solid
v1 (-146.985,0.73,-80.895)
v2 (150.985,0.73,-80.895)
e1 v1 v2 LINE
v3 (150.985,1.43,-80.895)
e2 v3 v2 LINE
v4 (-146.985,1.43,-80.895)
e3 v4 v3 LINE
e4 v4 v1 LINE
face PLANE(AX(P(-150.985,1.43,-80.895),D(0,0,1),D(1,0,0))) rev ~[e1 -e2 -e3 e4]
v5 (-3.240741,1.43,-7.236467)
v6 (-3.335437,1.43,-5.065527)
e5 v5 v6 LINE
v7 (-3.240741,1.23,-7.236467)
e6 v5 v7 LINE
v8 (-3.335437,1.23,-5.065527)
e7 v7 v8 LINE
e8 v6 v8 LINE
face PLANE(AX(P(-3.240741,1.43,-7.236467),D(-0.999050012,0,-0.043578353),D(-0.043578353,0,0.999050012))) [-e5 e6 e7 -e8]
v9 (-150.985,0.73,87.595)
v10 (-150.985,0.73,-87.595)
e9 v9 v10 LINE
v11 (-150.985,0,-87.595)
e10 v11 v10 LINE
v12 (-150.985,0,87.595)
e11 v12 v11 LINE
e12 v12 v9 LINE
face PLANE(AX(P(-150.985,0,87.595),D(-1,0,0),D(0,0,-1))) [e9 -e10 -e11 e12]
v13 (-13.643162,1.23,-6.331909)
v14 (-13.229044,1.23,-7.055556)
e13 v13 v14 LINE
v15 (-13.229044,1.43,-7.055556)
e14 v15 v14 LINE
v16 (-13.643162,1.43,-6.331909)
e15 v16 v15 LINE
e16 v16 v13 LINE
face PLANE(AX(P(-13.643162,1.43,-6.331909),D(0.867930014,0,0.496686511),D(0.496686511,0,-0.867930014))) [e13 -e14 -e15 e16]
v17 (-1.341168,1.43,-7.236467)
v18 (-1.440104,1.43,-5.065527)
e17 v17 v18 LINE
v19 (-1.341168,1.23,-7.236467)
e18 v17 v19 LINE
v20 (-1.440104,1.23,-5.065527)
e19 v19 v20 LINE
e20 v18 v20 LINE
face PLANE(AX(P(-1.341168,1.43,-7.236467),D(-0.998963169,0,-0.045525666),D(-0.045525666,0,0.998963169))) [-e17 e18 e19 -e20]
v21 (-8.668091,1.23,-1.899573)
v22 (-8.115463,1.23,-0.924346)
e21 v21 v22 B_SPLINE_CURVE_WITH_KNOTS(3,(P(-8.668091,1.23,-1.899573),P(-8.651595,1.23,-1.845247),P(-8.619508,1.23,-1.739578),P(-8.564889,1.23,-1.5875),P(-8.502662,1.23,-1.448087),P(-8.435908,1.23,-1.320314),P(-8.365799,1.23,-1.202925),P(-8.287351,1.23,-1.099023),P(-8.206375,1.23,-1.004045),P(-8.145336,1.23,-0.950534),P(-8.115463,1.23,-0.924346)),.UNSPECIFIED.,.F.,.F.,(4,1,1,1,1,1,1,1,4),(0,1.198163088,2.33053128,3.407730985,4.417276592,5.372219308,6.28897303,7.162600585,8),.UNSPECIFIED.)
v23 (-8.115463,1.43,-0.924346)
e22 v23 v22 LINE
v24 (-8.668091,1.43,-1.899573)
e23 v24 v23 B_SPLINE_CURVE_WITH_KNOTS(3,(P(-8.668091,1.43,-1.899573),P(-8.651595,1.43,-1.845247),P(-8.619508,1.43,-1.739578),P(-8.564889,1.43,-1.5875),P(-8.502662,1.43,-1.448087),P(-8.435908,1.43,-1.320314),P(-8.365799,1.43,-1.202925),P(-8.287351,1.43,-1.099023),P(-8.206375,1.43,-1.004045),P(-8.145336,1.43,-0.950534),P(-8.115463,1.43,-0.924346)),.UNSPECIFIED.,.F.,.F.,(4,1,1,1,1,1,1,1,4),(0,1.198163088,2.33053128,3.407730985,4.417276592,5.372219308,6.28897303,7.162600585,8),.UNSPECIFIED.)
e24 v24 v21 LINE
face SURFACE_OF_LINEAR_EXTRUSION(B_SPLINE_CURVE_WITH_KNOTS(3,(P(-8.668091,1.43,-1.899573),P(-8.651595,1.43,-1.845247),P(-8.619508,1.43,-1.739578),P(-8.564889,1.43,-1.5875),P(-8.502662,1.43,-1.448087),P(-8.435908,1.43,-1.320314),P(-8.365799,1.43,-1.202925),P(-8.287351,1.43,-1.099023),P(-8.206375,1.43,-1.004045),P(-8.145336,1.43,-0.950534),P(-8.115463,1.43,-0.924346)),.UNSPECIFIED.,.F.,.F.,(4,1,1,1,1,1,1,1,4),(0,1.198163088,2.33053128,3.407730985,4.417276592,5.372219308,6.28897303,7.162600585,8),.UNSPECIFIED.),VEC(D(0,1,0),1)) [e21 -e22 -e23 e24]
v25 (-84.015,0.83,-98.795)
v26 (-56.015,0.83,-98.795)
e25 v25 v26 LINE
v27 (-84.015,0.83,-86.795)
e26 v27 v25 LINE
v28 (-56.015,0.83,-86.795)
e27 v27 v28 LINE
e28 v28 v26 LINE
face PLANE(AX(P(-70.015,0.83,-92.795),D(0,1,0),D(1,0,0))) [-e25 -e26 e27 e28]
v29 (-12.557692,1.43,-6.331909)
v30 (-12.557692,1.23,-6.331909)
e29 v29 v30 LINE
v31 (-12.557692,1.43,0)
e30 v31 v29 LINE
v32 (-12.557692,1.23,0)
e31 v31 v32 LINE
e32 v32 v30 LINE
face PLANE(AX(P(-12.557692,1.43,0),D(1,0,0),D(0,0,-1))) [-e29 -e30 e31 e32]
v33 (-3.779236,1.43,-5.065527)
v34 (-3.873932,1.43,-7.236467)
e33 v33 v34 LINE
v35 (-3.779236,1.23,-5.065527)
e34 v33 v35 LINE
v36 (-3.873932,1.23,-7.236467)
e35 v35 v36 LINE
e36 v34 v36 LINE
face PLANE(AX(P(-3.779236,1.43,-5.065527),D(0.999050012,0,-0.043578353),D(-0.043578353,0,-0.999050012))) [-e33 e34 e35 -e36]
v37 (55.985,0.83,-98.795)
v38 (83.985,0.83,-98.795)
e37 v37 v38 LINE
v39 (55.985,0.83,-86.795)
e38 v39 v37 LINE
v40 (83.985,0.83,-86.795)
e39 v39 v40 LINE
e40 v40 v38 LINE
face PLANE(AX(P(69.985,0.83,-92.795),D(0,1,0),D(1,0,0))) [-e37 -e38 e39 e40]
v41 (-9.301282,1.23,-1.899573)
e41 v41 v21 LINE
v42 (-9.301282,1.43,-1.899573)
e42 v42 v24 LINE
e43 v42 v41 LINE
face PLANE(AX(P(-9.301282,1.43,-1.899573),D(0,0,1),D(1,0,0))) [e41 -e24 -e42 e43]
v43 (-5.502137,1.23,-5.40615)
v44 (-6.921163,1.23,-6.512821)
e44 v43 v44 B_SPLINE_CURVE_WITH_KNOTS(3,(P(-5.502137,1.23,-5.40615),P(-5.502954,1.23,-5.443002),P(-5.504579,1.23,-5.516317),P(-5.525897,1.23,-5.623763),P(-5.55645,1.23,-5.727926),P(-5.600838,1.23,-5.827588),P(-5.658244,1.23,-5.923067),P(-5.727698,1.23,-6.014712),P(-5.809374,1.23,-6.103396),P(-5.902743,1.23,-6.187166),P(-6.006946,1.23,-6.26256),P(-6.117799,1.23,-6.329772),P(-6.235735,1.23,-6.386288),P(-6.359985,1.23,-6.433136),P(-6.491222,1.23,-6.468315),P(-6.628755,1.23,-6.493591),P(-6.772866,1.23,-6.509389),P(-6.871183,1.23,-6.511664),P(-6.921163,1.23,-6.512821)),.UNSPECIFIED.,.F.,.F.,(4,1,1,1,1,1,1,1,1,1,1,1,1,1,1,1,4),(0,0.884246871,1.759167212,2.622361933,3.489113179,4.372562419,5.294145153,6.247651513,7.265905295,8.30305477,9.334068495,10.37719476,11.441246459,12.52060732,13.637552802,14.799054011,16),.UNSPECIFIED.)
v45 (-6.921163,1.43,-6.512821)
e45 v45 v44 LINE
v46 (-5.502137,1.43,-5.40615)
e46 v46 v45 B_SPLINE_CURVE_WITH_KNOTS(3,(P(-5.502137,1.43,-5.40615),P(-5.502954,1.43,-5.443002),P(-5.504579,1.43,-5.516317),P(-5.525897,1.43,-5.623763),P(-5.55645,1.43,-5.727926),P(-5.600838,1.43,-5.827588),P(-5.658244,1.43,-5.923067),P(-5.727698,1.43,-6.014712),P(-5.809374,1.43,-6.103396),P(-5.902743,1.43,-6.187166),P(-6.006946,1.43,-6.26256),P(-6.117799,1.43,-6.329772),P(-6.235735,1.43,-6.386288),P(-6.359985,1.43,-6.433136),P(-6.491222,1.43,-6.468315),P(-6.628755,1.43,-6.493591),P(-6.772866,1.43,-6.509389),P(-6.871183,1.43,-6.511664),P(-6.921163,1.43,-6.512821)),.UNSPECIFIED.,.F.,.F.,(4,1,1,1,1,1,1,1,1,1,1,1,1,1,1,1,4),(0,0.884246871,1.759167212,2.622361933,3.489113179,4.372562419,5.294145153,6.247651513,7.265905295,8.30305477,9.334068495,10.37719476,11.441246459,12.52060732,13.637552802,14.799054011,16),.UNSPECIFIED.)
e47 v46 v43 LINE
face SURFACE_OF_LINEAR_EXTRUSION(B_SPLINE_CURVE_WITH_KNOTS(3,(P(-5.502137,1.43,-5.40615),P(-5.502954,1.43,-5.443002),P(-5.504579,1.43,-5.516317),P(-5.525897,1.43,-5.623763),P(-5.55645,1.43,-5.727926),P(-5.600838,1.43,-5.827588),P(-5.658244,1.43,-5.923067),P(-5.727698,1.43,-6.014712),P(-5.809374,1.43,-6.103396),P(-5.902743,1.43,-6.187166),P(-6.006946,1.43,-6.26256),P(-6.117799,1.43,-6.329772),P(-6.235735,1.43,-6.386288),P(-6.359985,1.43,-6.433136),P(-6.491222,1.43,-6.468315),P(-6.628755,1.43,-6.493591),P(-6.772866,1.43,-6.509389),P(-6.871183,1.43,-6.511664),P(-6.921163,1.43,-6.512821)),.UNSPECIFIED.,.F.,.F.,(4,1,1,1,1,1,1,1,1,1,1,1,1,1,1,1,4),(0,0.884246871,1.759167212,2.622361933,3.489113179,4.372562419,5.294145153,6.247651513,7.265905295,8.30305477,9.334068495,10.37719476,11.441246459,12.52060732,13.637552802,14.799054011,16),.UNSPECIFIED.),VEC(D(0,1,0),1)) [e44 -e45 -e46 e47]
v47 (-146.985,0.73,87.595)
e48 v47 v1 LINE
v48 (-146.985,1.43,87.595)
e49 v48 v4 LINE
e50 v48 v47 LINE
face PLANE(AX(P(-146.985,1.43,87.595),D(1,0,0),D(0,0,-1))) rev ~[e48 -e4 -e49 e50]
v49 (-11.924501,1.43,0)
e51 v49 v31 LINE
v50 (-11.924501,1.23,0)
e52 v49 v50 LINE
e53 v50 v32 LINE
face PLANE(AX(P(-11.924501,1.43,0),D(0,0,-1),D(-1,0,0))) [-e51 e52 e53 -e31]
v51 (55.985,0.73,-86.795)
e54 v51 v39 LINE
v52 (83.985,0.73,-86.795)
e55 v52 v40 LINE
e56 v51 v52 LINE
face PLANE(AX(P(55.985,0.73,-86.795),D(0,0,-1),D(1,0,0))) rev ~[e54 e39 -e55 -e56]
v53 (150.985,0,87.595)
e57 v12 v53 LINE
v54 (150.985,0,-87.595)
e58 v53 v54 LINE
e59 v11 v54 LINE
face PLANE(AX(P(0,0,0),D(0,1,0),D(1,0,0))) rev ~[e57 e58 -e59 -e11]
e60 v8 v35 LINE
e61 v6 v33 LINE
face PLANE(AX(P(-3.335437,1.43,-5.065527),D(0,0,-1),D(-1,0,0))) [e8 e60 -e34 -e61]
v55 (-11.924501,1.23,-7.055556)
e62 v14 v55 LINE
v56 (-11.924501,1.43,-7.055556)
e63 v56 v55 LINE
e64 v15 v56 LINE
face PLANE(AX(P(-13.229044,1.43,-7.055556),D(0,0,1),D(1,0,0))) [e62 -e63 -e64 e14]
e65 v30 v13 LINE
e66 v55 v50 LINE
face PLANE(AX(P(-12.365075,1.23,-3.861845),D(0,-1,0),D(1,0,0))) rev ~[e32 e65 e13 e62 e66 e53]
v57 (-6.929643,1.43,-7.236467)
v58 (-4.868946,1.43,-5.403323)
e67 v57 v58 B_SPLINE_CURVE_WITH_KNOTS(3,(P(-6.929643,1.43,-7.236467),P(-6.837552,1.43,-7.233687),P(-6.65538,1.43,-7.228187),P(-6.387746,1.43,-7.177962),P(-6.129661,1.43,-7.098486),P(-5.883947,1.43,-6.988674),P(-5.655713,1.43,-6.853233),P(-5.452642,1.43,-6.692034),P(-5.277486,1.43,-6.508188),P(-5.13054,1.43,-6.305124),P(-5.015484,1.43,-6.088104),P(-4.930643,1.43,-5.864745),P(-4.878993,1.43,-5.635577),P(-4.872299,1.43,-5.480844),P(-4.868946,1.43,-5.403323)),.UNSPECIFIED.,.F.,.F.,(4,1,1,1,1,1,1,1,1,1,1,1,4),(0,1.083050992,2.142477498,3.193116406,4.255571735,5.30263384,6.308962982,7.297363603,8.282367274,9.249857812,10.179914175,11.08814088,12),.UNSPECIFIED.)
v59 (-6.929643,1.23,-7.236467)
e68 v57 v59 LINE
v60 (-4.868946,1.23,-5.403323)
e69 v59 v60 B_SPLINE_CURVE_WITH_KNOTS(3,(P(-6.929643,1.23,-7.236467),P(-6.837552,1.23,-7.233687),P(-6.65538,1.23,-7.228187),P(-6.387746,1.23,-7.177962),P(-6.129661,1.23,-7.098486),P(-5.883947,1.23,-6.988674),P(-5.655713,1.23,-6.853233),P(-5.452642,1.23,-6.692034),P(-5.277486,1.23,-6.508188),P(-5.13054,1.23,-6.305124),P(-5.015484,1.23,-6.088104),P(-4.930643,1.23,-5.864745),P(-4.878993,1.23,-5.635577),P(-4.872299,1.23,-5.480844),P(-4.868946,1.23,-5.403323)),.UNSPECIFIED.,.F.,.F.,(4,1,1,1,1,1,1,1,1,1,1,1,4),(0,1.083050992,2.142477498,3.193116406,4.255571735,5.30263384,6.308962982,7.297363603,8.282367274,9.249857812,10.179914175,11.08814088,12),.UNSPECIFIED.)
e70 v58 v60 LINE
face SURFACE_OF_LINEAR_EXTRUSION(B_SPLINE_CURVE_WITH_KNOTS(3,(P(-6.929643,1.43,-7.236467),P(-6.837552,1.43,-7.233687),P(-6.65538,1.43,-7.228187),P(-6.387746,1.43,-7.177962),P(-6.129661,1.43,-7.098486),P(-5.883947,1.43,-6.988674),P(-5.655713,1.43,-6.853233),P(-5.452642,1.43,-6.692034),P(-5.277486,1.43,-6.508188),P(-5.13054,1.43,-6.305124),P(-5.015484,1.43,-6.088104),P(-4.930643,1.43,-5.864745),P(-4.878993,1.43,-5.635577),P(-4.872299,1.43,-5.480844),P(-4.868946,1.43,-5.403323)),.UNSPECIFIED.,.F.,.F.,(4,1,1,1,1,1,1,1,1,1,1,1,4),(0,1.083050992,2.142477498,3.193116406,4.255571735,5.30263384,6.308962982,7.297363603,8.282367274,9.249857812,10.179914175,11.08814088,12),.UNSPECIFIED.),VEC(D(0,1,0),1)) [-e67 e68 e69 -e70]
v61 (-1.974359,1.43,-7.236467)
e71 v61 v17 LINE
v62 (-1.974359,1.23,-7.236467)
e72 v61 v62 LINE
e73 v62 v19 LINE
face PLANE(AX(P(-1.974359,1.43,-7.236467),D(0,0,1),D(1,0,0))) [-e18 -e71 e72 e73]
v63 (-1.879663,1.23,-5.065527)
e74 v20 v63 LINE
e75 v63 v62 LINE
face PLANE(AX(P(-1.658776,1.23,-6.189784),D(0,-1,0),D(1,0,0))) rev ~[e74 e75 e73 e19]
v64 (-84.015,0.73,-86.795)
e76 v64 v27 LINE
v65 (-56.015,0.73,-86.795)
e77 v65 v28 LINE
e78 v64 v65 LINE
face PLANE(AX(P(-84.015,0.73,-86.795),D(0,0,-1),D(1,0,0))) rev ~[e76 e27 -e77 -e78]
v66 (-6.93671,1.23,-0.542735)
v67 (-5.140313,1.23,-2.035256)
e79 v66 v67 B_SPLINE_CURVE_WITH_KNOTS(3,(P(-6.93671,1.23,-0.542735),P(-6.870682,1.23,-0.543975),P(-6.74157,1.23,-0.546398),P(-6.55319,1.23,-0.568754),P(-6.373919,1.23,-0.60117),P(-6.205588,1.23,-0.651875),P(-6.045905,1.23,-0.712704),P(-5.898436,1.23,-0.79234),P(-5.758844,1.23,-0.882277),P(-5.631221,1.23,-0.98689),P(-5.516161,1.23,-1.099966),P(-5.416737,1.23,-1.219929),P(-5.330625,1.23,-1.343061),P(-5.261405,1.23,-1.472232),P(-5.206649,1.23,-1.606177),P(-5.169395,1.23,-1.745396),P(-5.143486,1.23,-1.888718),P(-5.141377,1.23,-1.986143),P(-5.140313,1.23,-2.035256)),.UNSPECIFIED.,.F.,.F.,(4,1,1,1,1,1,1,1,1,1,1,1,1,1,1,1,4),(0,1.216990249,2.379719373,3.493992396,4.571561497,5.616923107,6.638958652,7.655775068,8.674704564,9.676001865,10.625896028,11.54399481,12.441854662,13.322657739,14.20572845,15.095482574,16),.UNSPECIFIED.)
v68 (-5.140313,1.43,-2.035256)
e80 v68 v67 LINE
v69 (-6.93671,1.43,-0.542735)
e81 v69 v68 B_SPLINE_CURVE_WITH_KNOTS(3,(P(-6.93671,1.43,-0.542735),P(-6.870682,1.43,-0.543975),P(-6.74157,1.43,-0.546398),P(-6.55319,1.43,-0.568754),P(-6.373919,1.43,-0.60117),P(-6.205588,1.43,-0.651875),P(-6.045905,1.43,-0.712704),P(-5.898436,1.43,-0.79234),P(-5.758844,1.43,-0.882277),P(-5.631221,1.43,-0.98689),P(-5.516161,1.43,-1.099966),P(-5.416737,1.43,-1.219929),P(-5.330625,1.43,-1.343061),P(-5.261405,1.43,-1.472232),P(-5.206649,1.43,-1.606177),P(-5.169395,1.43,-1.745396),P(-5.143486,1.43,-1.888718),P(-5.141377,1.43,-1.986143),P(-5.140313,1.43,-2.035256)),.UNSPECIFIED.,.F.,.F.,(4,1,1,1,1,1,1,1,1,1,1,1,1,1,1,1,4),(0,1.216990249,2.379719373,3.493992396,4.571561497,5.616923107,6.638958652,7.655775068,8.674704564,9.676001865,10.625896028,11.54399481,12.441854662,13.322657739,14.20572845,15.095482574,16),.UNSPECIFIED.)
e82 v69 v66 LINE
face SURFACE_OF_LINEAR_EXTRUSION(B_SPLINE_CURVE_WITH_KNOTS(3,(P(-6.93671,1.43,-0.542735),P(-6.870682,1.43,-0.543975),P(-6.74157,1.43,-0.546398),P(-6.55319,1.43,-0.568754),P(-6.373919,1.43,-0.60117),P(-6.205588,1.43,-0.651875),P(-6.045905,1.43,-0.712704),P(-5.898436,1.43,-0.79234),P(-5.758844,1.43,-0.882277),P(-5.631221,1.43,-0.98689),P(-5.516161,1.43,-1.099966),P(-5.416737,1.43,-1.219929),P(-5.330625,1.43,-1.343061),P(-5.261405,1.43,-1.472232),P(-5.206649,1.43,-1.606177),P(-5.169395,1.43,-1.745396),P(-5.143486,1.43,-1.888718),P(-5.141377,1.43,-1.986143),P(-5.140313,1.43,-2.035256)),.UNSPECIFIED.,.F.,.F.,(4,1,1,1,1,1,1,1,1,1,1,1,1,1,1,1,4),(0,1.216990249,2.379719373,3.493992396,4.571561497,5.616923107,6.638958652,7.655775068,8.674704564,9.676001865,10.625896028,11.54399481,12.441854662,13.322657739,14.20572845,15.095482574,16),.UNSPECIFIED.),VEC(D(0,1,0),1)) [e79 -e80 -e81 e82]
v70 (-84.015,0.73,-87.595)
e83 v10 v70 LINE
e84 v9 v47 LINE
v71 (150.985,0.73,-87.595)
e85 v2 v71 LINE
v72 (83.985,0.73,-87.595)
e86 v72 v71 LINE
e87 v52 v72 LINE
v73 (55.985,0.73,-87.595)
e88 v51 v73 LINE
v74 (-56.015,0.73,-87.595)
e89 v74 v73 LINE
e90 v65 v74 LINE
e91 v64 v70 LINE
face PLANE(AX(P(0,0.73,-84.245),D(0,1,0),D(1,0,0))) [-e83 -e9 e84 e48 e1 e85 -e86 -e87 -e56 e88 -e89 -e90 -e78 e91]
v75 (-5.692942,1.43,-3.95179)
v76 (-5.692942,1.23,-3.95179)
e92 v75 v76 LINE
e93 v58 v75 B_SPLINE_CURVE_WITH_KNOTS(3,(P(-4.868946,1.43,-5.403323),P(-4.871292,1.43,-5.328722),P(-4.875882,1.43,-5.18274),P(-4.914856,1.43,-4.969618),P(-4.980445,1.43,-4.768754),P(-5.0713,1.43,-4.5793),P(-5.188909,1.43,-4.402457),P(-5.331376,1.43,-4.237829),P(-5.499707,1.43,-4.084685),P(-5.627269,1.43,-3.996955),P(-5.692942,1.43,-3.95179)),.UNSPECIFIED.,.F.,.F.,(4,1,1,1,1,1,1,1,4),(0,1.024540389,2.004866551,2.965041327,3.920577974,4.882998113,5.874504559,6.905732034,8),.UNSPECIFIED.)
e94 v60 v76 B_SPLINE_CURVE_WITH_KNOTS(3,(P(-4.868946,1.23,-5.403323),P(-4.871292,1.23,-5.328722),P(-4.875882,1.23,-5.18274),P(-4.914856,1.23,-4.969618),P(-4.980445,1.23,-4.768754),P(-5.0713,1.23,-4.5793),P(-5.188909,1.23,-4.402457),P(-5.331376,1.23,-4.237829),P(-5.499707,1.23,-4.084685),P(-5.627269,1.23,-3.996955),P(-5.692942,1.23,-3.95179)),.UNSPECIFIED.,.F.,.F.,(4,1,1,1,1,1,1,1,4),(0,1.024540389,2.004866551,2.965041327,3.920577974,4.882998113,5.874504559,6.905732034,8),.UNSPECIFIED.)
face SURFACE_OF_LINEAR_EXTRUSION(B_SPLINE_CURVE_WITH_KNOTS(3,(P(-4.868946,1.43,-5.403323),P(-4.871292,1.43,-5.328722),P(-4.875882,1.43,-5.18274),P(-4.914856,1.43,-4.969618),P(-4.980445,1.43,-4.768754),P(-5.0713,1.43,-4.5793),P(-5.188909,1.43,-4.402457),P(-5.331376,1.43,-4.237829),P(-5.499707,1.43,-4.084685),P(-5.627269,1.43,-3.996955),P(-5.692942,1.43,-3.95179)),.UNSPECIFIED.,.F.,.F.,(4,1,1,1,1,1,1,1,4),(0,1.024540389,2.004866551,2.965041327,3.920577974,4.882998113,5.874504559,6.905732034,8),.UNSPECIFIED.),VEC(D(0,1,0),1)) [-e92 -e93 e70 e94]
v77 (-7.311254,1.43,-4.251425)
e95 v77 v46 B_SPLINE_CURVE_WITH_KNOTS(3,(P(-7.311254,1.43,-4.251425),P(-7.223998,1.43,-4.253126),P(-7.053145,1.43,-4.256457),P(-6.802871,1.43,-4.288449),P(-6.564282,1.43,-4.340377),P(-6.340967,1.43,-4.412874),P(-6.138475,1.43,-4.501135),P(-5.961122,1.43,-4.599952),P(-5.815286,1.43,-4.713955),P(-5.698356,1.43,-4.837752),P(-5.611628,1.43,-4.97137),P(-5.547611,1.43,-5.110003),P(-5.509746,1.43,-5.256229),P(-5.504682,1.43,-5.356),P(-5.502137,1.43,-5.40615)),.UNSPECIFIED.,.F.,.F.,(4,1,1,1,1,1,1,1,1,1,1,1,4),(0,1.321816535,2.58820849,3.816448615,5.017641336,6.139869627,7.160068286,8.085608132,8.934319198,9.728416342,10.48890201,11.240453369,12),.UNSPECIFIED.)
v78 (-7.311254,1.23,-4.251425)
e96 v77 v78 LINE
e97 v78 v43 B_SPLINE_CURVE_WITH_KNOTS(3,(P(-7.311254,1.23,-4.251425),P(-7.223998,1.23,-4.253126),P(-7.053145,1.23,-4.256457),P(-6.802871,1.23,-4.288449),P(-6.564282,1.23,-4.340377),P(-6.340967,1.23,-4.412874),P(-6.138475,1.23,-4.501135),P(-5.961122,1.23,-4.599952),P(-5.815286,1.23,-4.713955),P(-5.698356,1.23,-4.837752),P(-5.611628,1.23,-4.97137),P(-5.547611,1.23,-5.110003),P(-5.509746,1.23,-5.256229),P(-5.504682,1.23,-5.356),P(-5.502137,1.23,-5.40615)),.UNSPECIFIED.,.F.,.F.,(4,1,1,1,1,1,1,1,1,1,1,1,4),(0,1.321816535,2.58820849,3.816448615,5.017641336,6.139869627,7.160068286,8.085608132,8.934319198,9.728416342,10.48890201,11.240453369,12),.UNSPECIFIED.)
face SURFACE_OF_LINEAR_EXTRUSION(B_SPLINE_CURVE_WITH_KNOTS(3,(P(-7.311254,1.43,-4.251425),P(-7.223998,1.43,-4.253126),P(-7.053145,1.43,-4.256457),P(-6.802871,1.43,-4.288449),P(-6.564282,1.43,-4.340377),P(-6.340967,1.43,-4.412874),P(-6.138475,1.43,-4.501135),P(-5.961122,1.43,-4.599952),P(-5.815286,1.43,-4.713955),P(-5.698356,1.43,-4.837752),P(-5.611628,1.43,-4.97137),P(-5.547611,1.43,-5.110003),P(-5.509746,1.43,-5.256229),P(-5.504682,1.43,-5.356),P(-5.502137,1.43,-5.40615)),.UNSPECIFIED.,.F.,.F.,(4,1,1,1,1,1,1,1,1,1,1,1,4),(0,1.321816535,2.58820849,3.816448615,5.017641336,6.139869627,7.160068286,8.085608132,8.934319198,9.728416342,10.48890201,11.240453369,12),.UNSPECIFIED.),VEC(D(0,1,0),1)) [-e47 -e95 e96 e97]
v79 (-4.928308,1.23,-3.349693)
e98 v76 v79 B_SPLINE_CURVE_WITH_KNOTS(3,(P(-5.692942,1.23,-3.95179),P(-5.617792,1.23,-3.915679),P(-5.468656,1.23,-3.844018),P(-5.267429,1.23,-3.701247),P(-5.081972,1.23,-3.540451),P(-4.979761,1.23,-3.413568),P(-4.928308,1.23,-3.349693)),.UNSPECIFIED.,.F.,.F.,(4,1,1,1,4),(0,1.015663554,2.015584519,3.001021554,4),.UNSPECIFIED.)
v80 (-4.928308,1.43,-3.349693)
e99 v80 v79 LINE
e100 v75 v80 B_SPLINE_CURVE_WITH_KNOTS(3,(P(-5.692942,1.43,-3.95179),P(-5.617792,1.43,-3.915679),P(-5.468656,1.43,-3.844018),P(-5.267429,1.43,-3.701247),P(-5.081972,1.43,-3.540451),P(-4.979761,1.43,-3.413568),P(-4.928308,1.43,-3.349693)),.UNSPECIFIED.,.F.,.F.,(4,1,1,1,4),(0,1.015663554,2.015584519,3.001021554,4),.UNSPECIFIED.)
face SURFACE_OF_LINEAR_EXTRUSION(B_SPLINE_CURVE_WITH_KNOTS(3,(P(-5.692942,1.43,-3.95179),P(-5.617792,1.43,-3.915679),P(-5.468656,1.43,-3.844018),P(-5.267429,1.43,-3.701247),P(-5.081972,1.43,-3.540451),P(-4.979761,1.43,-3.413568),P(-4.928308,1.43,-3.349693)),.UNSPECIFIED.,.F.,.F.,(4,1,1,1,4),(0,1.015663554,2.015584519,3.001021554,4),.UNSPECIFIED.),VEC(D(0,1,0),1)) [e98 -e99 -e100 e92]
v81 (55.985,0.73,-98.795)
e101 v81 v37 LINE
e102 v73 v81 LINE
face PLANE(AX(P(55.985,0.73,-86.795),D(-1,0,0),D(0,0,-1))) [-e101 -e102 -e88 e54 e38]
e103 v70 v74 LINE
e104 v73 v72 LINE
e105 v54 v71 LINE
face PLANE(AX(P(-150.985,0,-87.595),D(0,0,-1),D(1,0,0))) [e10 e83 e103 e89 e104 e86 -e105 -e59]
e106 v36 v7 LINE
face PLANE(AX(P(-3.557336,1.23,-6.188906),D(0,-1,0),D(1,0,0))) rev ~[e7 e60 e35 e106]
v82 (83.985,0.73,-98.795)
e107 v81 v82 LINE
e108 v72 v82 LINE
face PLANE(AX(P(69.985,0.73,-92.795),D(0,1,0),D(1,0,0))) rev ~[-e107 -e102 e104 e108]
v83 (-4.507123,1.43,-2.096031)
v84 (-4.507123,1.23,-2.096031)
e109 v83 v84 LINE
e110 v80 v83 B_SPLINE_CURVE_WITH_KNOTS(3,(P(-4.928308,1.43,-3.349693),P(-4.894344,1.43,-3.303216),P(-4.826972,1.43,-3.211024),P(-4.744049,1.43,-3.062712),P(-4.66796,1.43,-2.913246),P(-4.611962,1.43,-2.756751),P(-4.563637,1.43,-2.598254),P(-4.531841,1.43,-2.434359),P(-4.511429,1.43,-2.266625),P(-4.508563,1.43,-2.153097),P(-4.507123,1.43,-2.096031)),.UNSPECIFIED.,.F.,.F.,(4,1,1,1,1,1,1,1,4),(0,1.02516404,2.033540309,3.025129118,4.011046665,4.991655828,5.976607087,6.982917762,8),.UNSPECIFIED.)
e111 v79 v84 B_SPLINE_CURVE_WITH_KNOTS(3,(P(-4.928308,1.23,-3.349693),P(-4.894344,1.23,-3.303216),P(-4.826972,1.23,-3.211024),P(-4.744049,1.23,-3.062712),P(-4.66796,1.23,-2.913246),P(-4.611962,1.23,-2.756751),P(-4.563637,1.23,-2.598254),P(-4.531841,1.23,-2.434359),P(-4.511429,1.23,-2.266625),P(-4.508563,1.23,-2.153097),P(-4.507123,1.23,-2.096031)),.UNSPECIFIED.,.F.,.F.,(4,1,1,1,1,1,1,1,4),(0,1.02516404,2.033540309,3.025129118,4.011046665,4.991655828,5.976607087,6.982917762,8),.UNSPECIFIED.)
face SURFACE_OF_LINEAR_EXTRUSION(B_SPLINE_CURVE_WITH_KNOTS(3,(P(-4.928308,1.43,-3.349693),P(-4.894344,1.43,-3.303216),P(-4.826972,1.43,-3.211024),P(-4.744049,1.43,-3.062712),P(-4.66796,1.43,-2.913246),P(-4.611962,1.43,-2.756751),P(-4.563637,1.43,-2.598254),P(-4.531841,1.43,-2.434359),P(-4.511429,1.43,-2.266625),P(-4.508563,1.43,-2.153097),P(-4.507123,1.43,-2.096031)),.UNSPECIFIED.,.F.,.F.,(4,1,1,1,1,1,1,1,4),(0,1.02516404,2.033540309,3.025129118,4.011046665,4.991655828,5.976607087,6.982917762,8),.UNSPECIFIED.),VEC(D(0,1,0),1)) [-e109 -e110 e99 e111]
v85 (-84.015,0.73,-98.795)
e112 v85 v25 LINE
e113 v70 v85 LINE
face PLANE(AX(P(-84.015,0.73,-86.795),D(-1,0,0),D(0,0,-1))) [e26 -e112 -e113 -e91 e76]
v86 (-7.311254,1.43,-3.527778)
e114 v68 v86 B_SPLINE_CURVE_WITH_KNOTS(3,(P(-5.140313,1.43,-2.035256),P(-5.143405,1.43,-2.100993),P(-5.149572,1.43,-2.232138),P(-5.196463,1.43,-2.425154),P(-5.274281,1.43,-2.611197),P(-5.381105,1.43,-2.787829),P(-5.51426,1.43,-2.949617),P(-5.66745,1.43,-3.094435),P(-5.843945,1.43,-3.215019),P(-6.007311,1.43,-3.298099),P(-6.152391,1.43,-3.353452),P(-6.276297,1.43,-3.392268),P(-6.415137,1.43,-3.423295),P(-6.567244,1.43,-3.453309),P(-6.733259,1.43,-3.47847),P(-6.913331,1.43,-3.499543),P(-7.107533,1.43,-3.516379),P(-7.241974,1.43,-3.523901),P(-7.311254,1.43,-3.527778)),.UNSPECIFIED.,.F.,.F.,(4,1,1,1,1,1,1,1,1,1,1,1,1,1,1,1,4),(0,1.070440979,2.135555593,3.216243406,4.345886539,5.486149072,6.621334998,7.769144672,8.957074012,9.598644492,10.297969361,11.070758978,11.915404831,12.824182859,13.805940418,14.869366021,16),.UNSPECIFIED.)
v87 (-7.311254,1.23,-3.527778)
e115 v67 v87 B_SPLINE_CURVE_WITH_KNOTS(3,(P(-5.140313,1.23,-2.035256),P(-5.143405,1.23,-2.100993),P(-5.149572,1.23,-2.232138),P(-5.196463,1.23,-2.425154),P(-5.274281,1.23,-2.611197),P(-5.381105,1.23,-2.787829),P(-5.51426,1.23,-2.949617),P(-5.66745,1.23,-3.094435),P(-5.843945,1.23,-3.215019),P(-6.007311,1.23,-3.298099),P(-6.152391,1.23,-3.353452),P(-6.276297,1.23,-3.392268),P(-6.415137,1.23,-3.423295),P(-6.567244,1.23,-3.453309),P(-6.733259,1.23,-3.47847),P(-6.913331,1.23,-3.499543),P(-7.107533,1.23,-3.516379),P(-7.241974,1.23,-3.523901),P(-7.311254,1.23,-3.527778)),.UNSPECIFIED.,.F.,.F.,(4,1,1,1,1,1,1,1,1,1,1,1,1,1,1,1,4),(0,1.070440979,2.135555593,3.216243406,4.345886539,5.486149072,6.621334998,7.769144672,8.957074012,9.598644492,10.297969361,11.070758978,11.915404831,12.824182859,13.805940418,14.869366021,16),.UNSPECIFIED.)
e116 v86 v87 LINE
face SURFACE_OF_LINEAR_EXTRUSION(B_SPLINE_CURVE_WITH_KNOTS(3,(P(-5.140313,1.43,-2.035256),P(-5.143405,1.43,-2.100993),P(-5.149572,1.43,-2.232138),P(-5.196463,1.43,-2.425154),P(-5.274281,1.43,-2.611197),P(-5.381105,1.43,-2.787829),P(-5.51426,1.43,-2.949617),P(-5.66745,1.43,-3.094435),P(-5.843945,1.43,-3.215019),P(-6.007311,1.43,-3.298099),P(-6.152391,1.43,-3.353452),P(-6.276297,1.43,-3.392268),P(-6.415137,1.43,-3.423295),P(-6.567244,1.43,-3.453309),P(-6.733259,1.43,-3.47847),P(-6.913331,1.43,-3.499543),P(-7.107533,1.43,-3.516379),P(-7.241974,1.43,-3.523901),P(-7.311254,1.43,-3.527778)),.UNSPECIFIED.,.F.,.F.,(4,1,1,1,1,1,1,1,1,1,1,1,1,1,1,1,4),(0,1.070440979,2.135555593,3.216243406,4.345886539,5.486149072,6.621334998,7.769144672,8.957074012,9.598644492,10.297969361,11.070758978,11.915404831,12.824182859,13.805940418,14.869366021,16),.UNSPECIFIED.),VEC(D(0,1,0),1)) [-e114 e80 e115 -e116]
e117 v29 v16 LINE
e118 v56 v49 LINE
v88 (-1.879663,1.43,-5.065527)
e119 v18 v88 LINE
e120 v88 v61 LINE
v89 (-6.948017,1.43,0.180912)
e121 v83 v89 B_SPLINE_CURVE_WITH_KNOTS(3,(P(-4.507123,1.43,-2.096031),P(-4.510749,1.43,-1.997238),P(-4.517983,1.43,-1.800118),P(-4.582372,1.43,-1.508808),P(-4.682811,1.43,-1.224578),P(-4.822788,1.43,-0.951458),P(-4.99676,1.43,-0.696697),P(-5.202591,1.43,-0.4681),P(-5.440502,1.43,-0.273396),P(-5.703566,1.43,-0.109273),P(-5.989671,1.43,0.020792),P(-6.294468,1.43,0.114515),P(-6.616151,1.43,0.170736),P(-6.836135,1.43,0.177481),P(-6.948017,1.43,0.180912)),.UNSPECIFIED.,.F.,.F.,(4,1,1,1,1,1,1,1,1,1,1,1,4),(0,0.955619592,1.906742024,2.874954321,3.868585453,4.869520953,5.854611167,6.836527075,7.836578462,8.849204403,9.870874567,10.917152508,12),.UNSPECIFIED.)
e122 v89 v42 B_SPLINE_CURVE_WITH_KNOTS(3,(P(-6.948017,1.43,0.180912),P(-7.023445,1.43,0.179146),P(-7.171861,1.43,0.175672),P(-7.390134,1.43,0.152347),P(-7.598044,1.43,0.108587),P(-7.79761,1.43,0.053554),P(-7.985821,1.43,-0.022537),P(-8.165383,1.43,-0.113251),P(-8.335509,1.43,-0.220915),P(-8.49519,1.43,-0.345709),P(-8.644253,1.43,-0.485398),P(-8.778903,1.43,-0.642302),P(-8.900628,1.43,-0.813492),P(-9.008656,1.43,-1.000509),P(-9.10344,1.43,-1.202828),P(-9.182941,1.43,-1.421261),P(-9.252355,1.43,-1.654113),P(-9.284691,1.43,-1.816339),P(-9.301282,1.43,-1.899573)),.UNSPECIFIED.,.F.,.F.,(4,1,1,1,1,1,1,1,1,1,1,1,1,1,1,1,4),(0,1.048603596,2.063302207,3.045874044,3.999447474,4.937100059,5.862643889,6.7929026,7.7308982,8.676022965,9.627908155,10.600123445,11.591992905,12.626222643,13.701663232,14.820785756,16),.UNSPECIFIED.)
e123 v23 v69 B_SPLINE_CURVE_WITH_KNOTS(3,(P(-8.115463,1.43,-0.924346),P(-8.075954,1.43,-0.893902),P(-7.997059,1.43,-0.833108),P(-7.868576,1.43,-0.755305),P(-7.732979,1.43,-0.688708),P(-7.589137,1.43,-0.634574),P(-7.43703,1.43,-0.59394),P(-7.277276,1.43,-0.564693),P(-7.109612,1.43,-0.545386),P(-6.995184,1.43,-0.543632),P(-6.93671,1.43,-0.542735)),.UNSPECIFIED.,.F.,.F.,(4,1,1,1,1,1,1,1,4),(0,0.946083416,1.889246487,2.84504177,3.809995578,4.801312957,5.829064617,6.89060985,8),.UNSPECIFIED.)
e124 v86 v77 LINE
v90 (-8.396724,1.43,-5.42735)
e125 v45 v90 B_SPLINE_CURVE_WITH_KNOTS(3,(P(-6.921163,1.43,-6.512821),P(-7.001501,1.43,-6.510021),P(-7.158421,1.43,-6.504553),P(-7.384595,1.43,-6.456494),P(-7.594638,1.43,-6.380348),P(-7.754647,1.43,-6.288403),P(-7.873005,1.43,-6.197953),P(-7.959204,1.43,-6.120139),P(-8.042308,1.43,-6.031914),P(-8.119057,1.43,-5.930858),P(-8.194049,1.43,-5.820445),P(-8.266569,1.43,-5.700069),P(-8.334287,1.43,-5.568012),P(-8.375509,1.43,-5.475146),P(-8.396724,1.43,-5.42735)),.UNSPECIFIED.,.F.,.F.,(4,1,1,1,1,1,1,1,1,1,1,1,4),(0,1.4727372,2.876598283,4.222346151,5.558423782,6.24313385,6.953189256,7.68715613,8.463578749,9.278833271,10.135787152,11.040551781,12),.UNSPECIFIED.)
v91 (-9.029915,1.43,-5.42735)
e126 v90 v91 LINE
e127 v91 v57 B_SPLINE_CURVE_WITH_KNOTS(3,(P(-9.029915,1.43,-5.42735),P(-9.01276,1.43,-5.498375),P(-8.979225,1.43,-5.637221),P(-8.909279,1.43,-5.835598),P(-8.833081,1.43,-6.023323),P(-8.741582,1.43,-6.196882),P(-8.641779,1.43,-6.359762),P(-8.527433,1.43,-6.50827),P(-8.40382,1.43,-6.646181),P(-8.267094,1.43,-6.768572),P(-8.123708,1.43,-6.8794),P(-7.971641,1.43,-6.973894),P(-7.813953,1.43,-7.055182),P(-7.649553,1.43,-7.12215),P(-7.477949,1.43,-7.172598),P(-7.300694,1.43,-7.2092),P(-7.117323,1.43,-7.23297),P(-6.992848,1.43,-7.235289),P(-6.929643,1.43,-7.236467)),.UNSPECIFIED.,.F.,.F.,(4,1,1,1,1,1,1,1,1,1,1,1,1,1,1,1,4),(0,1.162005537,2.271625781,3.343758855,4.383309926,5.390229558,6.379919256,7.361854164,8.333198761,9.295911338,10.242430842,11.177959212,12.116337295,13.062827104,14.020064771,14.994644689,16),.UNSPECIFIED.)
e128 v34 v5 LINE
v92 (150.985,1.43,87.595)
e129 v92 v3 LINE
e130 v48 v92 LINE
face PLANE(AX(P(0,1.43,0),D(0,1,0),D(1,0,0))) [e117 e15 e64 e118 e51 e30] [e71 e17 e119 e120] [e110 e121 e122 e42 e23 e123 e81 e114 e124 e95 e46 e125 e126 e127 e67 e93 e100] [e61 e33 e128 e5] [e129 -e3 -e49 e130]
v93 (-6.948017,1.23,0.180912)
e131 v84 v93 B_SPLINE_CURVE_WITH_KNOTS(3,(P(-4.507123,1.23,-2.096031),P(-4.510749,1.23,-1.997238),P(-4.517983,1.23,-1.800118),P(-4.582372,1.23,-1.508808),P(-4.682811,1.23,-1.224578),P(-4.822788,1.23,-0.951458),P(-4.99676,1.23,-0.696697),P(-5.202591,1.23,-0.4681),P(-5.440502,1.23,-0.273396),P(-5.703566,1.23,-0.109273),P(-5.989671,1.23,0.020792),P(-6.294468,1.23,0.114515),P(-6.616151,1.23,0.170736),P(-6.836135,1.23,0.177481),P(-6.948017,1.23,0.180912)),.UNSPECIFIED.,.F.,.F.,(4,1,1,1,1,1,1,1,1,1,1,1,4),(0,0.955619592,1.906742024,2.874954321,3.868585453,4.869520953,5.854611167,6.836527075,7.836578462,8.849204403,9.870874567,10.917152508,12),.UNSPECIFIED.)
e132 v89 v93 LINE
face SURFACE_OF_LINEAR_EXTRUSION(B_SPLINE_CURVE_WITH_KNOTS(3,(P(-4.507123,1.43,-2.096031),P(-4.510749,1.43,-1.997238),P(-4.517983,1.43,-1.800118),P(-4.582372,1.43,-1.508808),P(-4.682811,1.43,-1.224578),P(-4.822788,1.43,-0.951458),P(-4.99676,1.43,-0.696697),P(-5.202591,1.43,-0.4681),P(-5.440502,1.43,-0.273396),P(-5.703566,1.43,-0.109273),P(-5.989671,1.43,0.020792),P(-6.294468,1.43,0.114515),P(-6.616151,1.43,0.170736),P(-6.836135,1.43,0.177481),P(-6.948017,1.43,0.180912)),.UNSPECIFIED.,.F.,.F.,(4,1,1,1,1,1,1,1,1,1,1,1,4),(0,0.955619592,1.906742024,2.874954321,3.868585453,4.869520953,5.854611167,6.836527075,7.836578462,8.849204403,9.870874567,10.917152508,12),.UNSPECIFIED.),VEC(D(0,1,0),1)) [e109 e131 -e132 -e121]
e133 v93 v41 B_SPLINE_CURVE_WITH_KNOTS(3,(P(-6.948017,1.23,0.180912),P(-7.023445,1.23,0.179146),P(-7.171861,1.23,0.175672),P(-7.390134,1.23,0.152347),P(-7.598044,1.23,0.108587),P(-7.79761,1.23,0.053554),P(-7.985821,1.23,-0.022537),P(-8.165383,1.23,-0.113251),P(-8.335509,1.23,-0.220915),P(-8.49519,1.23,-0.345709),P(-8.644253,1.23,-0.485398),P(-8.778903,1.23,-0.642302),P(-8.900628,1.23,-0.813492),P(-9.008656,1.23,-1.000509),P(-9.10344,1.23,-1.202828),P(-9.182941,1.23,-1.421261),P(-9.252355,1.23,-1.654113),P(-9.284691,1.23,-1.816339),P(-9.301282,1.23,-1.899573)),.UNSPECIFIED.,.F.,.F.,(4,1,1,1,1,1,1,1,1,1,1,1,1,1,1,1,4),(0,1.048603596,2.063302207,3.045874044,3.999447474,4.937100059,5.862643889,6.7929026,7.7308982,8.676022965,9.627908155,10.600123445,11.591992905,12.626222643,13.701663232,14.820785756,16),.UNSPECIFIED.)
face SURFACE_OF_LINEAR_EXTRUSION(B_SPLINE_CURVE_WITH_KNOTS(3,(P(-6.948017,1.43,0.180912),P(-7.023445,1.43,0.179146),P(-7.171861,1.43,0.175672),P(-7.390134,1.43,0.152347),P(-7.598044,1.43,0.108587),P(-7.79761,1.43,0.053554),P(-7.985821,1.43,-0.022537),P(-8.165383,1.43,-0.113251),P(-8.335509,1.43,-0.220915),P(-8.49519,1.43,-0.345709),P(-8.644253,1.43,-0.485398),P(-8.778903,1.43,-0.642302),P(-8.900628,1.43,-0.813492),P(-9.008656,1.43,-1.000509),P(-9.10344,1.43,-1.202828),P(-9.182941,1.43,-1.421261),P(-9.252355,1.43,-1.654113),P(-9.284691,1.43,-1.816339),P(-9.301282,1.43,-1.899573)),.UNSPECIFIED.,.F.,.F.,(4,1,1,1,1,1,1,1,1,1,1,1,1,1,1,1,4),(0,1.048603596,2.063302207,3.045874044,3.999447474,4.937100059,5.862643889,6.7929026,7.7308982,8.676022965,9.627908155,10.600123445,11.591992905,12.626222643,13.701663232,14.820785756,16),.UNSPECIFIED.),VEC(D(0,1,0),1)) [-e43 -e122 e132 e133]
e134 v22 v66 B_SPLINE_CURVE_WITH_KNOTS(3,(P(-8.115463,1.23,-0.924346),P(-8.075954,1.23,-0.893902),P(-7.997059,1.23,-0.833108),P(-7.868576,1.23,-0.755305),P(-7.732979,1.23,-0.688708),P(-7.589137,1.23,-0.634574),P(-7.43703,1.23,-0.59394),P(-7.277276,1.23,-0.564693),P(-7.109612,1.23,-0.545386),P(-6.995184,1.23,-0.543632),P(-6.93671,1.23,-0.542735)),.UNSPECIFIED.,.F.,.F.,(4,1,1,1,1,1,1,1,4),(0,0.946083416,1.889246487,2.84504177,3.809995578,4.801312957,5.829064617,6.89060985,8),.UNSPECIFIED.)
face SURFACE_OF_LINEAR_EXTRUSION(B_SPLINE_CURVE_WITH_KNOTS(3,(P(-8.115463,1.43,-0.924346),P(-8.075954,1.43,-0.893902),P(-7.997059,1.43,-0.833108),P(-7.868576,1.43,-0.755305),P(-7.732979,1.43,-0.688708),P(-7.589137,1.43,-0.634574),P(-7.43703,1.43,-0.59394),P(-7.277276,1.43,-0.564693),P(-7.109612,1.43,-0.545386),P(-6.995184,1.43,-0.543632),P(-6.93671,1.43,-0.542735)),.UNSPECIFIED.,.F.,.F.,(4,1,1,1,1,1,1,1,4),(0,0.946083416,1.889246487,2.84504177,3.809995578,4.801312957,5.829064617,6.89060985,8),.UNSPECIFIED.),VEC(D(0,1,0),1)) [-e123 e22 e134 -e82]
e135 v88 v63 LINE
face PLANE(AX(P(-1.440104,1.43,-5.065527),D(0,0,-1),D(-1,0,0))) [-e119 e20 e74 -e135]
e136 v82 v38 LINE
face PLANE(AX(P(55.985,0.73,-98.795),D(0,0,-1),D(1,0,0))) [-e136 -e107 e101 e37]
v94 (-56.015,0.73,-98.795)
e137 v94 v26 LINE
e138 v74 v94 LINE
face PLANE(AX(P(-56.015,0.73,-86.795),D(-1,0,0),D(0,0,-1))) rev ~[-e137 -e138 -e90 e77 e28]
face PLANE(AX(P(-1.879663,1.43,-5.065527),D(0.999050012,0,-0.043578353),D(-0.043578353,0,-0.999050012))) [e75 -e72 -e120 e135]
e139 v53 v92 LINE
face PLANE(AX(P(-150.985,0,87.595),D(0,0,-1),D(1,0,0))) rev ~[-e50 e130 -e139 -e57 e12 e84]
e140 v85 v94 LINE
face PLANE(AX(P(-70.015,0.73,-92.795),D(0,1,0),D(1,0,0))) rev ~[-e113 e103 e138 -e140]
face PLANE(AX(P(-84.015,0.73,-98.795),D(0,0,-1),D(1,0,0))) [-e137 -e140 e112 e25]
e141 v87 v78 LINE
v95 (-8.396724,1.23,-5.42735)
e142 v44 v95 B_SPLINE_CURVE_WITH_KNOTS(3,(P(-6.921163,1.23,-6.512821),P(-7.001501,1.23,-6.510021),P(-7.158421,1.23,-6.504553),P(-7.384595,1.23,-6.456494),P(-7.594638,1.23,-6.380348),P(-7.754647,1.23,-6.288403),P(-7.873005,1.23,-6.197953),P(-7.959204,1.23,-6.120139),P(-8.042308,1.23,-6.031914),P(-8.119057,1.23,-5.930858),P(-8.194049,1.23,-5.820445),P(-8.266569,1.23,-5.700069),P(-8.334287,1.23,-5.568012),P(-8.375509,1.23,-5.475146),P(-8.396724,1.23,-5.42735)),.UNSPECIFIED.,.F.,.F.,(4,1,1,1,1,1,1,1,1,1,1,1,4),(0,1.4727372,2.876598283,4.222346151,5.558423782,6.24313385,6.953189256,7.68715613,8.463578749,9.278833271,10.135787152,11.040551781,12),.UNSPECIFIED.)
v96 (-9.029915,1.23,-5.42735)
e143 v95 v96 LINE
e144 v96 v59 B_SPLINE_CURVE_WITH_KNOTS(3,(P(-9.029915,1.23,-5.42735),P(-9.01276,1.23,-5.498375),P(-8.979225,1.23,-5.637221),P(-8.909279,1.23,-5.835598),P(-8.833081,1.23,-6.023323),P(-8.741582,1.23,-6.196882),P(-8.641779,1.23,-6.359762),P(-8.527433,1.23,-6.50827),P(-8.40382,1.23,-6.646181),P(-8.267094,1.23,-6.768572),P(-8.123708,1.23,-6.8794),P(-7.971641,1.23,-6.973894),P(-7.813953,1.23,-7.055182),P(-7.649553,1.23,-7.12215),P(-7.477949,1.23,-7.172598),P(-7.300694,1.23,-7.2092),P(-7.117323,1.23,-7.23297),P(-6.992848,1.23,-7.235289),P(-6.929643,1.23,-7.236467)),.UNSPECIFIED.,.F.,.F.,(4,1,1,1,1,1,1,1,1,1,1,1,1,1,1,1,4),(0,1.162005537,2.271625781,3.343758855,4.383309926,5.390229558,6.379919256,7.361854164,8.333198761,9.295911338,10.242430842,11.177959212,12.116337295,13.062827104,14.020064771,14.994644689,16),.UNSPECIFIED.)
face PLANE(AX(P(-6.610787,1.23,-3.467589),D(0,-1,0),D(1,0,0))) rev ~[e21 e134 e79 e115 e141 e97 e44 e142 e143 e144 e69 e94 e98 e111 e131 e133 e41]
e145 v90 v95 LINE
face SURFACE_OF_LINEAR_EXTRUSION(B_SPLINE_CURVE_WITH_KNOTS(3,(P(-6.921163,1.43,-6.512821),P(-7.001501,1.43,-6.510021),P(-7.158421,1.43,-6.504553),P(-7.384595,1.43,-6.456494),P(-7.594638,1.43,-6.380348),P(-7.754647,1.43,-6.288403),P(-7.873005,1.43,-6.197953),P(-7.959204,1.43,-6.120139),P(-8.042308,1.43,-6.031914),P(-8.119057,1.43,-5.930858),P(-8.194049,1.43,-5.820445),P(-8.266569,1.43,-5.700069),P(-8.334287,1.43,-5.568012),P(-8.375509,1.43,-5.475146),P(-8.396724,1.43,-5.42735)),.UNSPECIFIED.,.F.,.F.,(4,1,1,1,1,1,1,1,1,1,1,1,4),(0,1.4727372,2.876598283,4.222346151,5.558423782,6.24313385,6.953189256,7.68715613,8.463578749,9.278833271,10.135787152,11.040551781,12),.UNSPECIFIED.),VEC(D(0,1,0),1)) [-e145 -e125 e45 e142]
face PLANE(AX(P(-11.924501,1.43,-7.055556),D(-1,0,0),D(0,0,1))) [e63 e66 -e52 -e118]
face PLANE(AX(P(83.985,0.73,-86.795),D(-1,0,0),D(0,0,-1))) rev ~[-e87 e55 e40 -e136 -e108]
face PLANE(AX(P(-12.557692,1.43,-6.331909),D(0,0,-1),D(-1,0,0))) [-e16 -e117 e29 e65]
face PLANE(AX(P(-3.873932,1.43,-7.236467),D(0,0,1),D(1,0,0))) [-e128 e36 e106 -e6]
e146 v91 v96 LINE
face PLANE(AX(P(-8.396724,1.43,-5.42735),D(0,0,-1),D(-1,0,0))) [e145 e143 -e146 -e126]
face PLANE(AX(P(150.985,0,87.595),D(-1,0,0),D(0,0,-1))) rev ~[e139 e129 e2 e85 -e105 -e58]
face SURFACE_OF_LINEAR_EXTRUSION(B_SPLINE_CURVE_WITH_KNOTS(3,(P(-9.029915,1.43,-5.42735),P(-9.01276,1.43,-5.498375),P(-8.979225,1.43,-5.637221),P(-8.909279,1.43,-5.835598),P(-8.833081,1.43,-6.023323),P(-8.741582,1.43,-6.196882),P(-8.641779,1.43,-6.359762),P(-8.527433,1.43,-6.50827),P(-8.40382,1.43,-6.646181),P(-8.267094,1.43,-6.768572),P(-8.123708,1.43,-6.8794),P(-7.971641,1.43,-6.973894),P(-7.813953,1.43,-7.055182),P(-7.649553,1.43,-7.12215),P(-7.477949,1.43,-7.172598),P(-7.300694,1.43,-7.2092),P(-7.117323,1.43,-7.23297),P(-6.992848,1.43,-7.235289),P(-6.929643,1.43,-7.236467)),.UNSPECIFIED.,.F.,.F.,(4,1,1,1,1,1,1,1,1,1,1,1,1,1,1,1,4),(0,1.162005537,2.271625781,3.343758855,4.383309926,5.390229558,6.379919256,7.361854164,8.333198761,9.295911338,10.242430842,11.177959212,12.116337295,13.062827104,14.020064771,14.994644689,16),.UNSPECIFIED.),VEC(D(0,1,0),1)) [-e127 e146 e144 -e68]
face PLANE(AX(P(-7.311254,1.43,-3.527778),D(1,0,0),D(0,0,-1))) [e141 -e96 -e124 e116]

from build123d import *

# Parameters (mm, degrees)
SKETCH_2_W             = 301.97
SKETCH_2_H             = 175.19
BOSS_EXTRUDE_1_DEPTH   = 1.43
CUT_EXTRUDE_2_DEPTH    = 0.2
SKETCH_5_W             = 301.97
SKETCH_5_H             = 6.7
CUT_EXTRUDE_3_DEPTH    = 0.7
SKETCH_6_W             = 4
SKETCH_6_H             = 168.49
CUT_EXTRUDE_4_DEPTH    = 0.7
SKETCH_7_W             = 28
SKETCH_7_H             = 12
BOSS_EXTRUDE_2_DEPTH   = 0.1
LINEAR_PATTERN_1_COUNT = 2
LINEAR_PATTERN_1_PITCH = 140


with BuildPart() as part:
    # Sketch 2 → Boss-Extrude 1 (new body)
    with BuildSketch(Plane(origin=(0, 0, 0), x_dir=(1, 0, 0), z_dir=(0, 1, 0))):
        Rectangle(SKETCH_2_W, SKETCH_2_H)
    extrude(amount=BOSS_EXTRUDE_1_DEPTH)

    # Sketch 4 → Cut-Extrude 2 (cut)
    with BuildSketch(Plane(origin=(0, 1.43, 0), x_dir=(-1, 0, 0), z_dir=(0, 1, 0))):
        Polygon((13.229044249, -7.055555556), (11.924501425, -7.055555556), (11.924501425, 0), (12.557692308, 0), (12.557692308, -6.331908832), (13.643162393, -6.331908832), align=None)
        with BuildLine():
            Line((8.396723647, -5.427350427), (9.02991453, -5.427350427))
            add(Edge.make_bspline(
                [(9.02991453, -5.427350427), (9.012760356, -5.498374641), (8.97922535, -5.63722117), (8.909279448, -5.835597711), (8.833080949, -6.023322905), (8.741582278, -6.196881657), (8.641778917, -6.359761985), (8.527433113, -6.508269585), (8.403820339, -6.646181436), (8.267093854, -6.768571613), (8.123707504, -6.879399734), (7.97164089, -6.973893897), (7.813953469, -7.055182269), (7.649552709, -7.122150038), (7.477949157, -7.172598316), (7.300694202, -7.20920013), (7.117323336, -7.232969519), (6.992848035, -7.235289311), (6.929642984, -7.236467236)],
                knots=[0, 0, 0, 0, 1.162005537, 2.271625781, 3.343758855, 4.383309926, 5.390229558, 6.379919256, 7.361854164, 8.333198761, 9.295911338, 10.242430842, 11.177959212, 12.116337295, 13.062827104, 14.020064771, 14.994644689, 16, 16, 16, 16], degree=3))
            add(Edge.make_bspline(
                [(6.929642984, -7.236467236), (6.837552377, -7.233686883), (6.655379927, -7.228186825), (6.387746483, -7.177962485), (6.129660673, -7.098486424), (5.883947427, -6.988674308), (5.655713444, -6.853233216), (5.452642084, -6.692034461), (5.277485879, -6.50818825), (5.13054007, -6.305124192), (5.01548412, -6.088104355), (4.930643335, -5.864745308), (4.87899328, -5.63557689), (4.872299459, -5.480843962), (4.868945869, -5.403323095)],
                knots=[0, 0, 0, 0, 1.083050992, 2.142477498, 3.193116406, 4.255571735, 5.30263384, 6.308962982, 7.297363603, 8.282367274, 9.249857812, 10.179914175, 11.08814088, 12, 12, 12, 12], degree=3))
            add(Edge.make_bspline(
                [(4.868945869, -5.403323095), (4.871291521, -5.328722096), (4.875881597, -5.182739518), (4.914855893, -4.969618405), (4.980444867, -4.768753591), (5.071299785, -4.579299503), (5.188908942, -4.402457365), (5.331376125, -4.237829299), (5.499706887, -4.084685124), (5.627269191, -3.996955392), (5.692942041, -3.95178953)],
                knots=[0, 0, 0, 0, 1.024540389, 2.004866551, 2.965041327, 3.920577974, 4.882998113, 5.874504559, 6.905732034, 8, 8, 8, 8], degree=3))
            add(Edge.make_bspline(
                [(5.692942041, -3.95178953), (5.617791884, -3.915679202), (5.468656385, -3.844018249), (5.267429073, -3.701247147), (5.081971807, -3.540451451), (4.979761436, -3.413567658), (4.928307514, -3.349692842)],
                knots=[0, 0, 0, 0, 1.015663554, 2.015584519, 3.001021554, 4, 4, 4, 4], degree=3))
            add(Edge.make_bspline(
                [(4.928307514, -3.349692842), (4.894343687, -3.303216296), (4.826972214, -3.21102429), (4.744048511, -3.062711825), (4.667960424, -2.913246469), (4.611961795, -2.756751438), (4.563637197, -2.598253629), (4.53184122, -2.43435897), (4.511429475, -2.2666246), (4.508563249, -2.153097273), (4.507122507, -2.096031428)],
                knots=[0, 0, 0, 0, 1.02516404, 2.033540309, 3.025129118, 4.011046665, 4.991655828, 5.976607087, 6.982917762, 8, 8, 8, 8], degree=3))
            add(Edge.make_bspline(
                [(4.507122507, -2.096031428), (4.510748504, -1.997238489), (4.517983434, -1.800117531), (4.582372301, -1.508808314), (4.68281079, -1.224578162), (4.822788474, -0.951458), (4.996759546, -0.696697491), (5.202590989, -0.468099979), (5.44050197, -0.273396385), (5.70356555, -0.109273381), (5.989671277, 0.020792248), (6.294467942, 0.114515076), (6.616150937, 0.170735628), (6.83613539, 0.177481044), (6.948016827, 0.180911681)],
                knots=[0, 0, 0, 0, 0.955619592, 1.906742024, 2.874954321, 3.868585453, 4.869520953, 5.854611167, 6.836527075, 7.836578462, 8.849204403, 9.870874567, 10.917152508, 12, 12, 12, 12], degree=3))
            add(Edge.make_bspline(
                [(6.948016827, 0.180911681), (7.023444636, 0.179146208), (7.171861413, 0.175672345), (7.390134183, 0.152347175), (7.598044238, 0.10858745), (7.797610468, 0.053553541), (7.985820933, -0.022537006), (8.165382865, -0.113251033), (8.335509182, -0.220914784), (8.495189558, -0.345709317), (8.644253397, -0.485398135), (8.778903044, -0.642301861), (8.900628256, -0.813492126), (9.008655605, -1.000508816), (9.103439737, -1.202828123), (9.18294089, -1.421260777), (9.252355217, -1.654113393), (9.28469129, -1.81633906), (9.301282051, -1.89957265)],
                knots=[0, 0, 0, 0, 1.048603596, 2.063302207, 3.045874044, 3.999447474, 4.937100059, 5.862643889, 6.7929026, 7.7308982, 8.676022965, 9.627908155, 10.600123445, 11.591992905, 12.626222643, 13.701663232, 14.820785756, 16, 16, 16, 16], degree=3))
            Line((9.301282051, -1.89957265), (8.668091168, -1.89957265))
            add(Edge.make_bspline(
                [(8.668091168, -1.89957265), (8.651594692, -1.845246861), (8.619507612, -1.739578483), (8.564888948, -1.587500407), (8.502662431, -1.448086553), (8.435907686, -1.320314228), (8.365798755, -1.202925099), (8.287351208, -1.099023236), (8.206375312, -1.004044972), (8.145335981, -0.950534405), (8.115462518, -0.92434562)],
                knots=[0, 0, 0, 0, 1.198163088, 2.33053128, 3.407730985, 4.417276592, 5.372219308, 6.28897303, 7.162600585, 8, 8, 8, 8], degree=3))
            add(Edge.make_bspline(
                [(8.115462518, -0.92434562), (8.075953896, -0.893901696), (7.997058605, -0.833107821), (7.86857617, -0.755304947), (7.73297924, -0.688707547), (7.589137035, -0.634574389), (7.437030258, -0.593940088), (7.277275918, -0.56469343), (7.109611898, -0.545386092), (6.99518448, -0.543631615), (6.936709847, -0.542735043)],
                knots=[0, 0, 0, 0, 0.946083416, 1.889246487, 2.84504177, 3.809995578, 4.801312957, 5.829064617, 6.89060985, 8, 8, 8, 8], degree=3))
            add(Edge.make_bspline(
                [(6.936709847, -0.542735043), (6.870682051, -0.54397461), (6.741570396, -0.546398478), (6.553189754, -0.568753907), (6.373919013, -0.601169975), (6.205587632, -0.651875009), (6.045905032, -0.712704074), (5.898435792, -0.792340483), (5.758844497, -0.882276933), (5.631220527, -0.986890322), (5.516161278, -1.099966072), (5.416737374, -1.219929365), (5.330624903, -1.34306056), (5.261404846, -1.472232057), (5.206648533, -1.606176788), (5.169395221, -1.74539611), (5.143486475, -1.888717708), (5.141376871, -1.986142971), (5.14031339, -2.03525641)],
                knots=[0, 0, 0, 0, 1.216990249, 2.379719373, 3.493992396, 4.571561497, 5.616923107, 6.638958652, 7.655775068, 8.674704564, 9.676001865, 10.625896028, 11.54399481, 12.441854662, 13.322657739, 14.20572845, 15.095482574, 16, 16, 16, 16], degree=3))
            add(Edge.make_bspline(
                [(5.14031339, -2.03525641), (5.143404721, -2.100992598), (5.149571999, -2.232137879), (5.196462724, -2.42515422), (5.274281053, -2.611196599), (5.381105148, -2.787828631), (5.514259527, -2.949617204), (5.667449989, -3.094435416), (5.843945137, -3.215018861), (6.007310827, -3.298099277), (6.152391001, -3.353452476), (6.276296829, -3.392267861), (6.415137166, -3.423295429), (6.567243737, -3.453308702), (6.733258521, -3.478469851), (6.913330944, -3.499543322), (7.107533493, -3.516378915), (7.241974144, -3.523901348), (7.311253561, -3.527777778)],
                knots=[0, 0, 0, 0, 1.070440979, 2.135555593, 3.216243406, 4.345886539, 5.486149072, 6.621334998, 7.769144672, 8.957074012, 9.598644492, 10.297969361, 11.070758978, 11.915404831, 12.824182859, 13.805940418, 14.869366021, 16, 16, 16, 16], degree=3))
            Line((7.311253561, -3.527777778), (7.311253561, -4.251424501))
            add(Edge.make_bspline(
                [(7.311253561, -4.251424501), (7.223997859, -4.2531257), (7.05314514, -4.256456766), (6.802871441, -4.288448854), (6.564282395, -4.340376533), (6.340966734, -4.412874319), (6.138475327, -4.501134643), (5.96112159, -4.59995249), (5.815285861, -4.713954565), (5.698356211, -4.837751832), (5.611628219, -4.971370396), (5.547610738, -5.110003022), (5.509745747, -5.256228753), (5.504682015, -5.35600018), (5.502136752, -5.40614984)],
                knots=[0, 0, 0, 0, 1.321816535, 2.58820849, 3.816448615, 5.017641336, 6.139869627, 7.160068286, 8.085608132, 8.934319198, 9.728416342, 10.48890201, 11.240453369, 12, 12, 12, 12], degree=3))
            add(Edge.make_bspline(
                [(5.502136752, -5.40614984), (5.502953772, -5.443001672), (5.504579194, -5.516316646), (5.525896555, -5.623762669), (5.55644982, -5.727925506), (5.600837525, -5.827588083), (5.65824432, -5.923067217), (5.727697997, -6.014711631), (5.809374488, -6.103396446), (5.902743403, -6.187165723), (6.006945503, -6.262559555), (6.117798524, -6.329772106), (6.235734636, -6.386288293), (6.359985283, -6.433136374), (6.491222098, -6.468315377), (6.628754675, -6.493590721), (6.772865741, -6.509389136), (6.871183225, -6.511664059), (6.921162749, -6.512820513)],
                knots=[0, 0, 0, 0, 0.884246871, 1.759167212, 2.622361933, 3.489113179, 4.372562419, 5.294145153, 6.247651513, 7.265905295, 8.30305477, 9.334068495, 10.37719476, 11.441246459, 12.52060732, 13.637552802, 14.799054011, 16, 16, 16, 16], degree=3))
            add(Edge.make_bspline(
                [(6.921162749, -6.512820513), (7.001501306, -6.510021144), (7.158421193, -6.504553326), (7.384595228, -6.456493672), (7.59463756, -6.380348103), (7.754647447, -6.288402555), (7.873004885, -6.197952768), (7.959203557, -6.120138816), (8.042307907, -6.031913732), (8.119056845, -5.930857602), (8.194049328, -5.820445336), (8.266569293, -5.700068826), (8.334287394, -5.568011861), (8.375508512, -5.475145598), (8.396723647, -5.427350427)],
                knots=[0, 0, 0, 0, 1.4727372, 2.876598283, 4.222346151, 5.558423782, 6.24313385, 6.953189256, 7.68715613, 8.463578749, 9.278833271, 10.135787152, 11.040551781, 12, 12, 12, 12], degree=3))
        make_face()
        Polygon((1.440104167, -5.065527066), (1.879663016, -5.065527066), (1.974358974, -7.236467236), (1.341168091, -7.236467236), align=None)
        Polygon((3.335436699, -5.065527066), (3.779235666, -5.065527066), (3.873931624, -7.236467236), (3.240740741, -7.236467236), align=None)
    extrude(amount=-CUT_EXTRUDE_2_DEPTH, mode=Mode.SUBTRACT)

    # Sketch 5 → Cut-Extrude 3 (cut)
    with BuildSketch(Plane(origin=(0, 1.43, 0), x_dir=(1, 0, 0), z_dir=(0, 1, 0))):
        with Locations((0, 84.245)):
            Rectangle(SKETCH_5_W, SKETCH_5_H)
    extrude(amount=-CUT_EXTRUDE_3_DEPTH, mode=Mode.SUBTRACT)

    # Sketch 6 → Cut-Extrude 4 (cut)
    with BuildSketch(Plane(origin=(0, 1.43, 0), x_dir=(1, 0, 0), z_dir=(0, 1, 0))):
        with Locations((-148.985, -3.35)):
            Rectangle(SKETCH_6_W, SKETCH_6_H)
    extrude(amount=-CUT_EXTRUDE_4_DEPTH, mode=Mode.SUBTRACT)

    # Sketch 7 → Boss-Extrude 2 (add)
    with BuildSketch(Plane(origin=(0, 0.73, 0), x_dir=(1, 0, 0), z_dir=(0, 1, 0))):
        with Locations((69.985, 92.795)):
            Rectangle(SKETCH_7_W, SKETCH_7_H)
    boss_extrude_2 = extrude(amount=BOSS_EXTRUDE_2_DEPTH)

    # Linear Pattern 1: Boss-Extrude 2 ×2
    with Locations(*[(-i * LINEAR_PATTERN_1_PITCH, 0, 0) for i in range(1, LINEAR_PATTERN_1_COUNT)]):
        add(boss_extrude_2)


solid = part.part
